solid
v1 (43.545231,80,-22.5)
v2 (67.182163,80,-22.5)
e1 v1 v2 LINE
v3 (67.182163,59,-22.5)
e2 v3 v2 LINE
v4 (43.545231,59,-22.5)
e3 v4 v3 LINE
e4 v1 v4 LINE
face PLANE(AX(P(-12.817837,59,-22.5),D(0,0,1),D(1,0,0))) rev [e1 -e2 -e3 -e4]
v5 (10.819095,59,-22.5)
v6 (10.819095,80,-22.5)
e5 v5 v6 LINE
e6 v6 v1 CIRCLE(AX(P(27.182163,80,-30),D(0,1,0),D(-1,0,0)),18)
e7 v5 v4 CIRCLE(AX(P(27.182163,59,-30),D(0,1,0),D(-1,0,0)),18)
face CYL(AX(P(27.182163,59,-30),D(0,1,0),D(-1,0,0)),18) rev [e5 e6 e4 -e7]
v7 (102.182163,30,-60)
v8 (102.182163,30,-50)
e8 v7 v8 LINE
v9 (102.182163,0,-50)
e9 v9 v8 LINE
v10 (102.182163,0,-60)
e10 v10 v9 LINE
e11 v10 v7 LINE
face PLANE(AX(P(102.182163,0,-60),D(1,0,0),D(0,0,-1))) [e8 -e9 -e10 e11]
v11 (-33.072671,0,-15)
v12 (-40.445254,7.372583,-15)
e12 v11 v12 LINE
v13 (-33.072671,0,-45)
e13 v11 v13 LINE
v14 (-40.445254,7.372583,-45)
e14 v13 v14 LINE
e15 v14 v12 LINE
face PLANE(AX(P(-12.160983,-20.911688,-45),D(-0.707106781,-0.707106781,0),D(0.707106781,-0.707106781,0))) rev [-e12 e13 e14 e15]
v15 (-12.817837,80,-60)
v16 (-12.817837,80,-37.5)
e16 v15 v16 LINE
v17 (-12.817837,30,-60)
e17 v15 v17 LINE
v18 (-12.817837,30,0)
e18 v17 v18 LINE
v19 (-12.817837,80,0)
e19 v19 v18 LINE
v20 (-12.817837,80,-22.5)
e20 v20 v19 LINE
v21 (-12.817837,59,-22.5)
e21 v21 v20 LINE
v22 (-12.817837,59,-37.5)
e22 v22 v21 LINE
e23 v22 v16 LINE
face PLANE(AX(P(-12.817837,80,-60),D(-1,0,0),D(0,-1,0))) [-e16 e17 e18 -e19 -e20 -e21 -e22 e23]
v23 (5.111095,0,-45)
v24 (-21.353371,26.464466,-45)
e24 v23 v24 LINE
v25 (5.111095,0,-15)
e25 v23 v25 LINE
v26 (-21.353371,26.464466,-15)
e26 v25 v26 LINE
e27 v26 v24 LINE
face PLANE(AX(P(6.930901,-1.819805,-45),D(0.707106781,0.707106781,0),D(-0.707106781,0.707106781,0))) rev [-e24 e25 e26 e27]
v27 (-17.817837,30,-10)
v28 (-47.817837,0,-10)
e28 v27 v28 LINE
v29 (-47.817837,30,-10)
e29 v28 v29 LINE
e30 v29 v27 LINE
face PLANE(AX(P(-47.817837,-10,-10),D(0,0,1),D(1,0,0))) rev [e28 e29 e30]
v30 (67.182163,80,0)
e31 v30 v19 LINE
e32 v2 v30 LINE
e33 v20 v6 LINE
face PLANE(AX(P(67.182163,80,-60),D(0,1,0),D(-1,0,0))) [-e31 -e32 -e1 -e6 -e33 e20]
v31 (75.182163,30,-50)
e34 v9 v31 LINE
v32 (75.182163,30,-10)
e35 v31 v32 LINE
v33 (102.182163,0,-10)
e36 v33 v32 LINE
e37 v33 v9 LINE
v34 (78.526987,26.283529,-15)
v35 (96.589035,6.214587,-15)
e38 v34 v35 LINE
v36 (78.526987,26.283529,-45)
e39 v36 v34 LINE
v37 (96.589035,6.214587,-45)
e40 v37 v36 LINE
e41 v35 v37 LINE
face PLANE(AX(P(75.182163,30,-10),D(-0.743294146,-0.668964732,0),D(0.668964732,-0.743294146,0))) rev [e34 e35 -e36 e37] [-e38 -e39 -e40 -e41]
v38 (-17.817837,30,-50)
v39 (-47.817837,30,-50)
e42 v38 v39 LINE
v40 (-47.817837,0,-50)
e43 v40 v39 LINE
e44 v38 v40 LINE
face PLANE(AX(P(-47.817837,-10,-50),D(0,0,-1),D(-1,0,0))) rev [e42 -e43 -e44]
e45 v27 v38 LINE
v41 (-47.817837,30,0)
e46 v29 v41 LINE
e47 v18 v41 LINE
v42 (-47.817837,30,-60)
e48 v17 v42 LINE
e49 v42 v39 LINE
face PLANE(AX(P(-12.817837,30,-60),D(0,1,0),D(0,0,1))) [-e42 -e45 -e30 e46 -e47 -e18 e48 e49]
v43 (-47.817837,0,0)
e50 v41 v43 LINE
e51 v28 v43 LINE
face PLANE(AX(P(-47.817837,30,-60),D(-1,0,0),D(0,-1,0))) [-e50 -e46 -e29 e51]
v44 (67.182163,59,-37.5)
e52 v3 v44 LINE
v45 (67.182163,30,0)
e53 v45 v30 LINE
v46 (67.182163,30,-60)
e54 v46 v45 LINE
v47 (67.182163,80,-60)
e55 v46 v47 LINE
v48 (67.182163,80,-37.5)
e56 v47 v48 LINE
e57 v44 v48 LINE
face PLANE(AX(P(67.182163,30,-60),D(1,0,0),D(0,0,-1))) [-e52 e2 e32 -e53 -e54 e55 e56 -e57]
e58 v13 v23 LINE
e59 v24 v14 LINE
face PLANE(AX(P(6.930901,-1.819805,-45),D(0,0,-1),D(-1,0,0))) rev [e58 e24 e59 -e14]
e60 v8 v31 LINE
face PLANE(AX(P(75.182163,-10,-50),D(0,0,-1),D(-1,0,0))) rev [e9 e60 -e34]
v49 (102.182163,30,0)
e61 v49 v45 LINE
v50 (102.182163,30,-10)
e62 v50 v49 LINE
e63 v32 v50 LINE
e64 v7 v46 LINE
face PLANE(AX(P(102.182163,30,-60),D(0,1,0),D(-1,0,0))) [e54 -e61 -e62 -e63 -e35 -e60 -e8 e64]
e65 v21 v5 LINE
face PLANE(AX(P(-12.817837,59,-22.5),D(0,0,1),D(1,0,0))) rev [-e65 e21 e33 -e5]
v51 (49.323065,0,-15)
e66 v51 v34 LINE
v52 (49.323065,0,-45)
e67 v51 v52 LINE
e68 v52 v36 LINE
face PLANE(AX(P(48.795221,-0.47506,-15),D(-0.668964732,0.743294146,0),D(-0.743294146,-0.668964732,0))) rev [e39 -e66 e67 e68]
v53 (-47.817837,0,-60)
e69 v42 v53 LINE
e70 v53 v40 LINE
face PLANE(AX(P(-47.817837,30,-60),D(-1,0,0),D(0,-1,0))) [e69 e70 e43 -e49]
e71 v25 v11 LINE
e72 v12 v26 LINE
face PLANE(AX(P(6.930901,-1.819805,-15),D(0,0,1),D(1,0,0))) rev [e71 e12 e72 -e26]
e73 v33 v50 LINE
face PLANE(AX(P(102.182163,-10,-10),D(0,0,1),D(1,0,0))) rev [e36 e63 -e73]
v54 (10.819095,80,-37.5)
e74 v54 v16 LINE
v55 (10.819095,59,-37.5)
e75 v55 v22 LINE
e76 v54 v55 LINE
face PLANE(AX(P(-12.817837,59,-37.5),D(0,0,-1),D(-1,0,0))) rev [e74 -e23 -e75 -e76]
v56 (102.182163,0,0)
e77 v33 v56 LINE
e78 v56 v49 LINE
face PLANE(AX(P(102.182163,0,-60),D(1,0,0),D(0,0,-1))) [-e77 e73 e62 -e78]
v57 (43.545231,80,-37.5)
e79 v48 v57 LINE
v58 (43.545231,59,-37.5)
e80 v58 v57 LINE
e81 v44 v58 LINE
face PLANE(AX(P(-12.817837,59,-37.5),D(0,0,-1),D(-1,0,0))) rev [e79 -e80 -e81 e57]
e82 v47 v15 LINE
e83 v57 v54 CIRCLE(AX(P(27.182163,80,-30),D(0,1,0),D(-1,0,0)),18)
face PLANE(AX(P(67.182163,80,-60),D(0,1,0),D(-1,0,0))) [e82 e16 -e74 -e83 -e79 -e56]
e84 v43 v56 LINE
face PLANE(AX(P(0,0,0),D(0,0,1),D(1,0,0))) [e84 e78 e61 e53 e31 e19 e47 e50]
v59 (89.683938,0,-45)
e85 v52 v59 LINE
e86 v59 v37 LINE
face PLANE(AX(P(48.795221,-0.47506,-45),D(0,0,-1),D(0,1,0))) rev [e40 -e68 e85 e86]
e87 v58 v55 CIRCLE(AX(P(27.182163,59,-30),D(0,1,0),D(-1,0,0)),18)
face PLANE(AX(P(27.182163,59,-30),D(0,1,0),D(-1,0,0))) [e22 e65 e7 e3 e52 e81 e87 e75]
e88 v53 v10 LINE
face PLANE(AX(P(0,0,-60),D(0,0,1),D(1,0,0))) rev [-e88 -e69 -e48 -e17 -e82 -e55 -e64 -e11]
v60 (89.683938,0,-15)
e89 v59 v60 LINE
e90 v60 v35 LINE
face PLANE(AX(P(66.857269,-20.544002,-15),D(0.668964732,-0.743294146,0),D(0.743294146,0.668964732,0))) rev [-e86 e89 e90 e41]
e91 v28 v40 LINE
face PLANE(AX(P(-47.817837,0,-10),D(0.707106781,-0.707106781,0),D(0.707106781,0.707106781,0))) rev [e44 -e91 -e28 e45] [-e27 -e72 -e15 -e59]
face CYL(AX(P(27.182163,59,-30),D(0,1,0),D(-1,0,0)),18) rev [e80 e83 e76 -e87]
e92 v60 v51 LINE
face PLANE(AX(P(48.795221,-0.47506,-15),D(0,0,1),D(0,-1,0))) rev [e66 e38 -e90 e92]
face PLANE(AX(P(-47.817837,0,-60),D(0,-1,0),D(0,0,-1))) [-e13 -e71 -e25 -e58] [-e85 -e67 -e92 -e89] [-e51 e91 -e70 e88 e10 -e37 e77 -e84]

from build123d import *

# Parameters (mm, degrees)
BASE_BLOCK_DEPTH           = 60
BORE_SKETCH_R              = 18
HALF_BORE_CUT_DEPTH        = 21
TOP_SLOT_SKETCH_W          = 80
TOP_SLOT_SKETCH_H          = 15
TOP_SLOT_CUT_DEPTH         = 21
SIDE_POCKET_A_SKETCH_W     = 27
SIDE_POCKET_A_SKETCH_H     = 40
SIDE_POCKET_A_DEPTH        = 40
FRAME_INFILL_A_DEPTH       = 40
TRIANGLE_WINDOW_A_SKETCH_W = 30
TRIANGLE_WINDOW_A_SKETCH_H = 27
TRIANGLE_WINDOW_A_DEPTH    = 40
SIDE_POCKET_B_SKETCH_W     = 30
SIDE_POCKET_B_SKETCH_H     = 40
SIDE_POCKET_B_DEPTH        = 40
FRAME_INFILL_B_DEPTH       = 40
TRIANGLE_WINDOW_B_SKETCH_W = 30
TRIANGLE_WINDOW_B_SKETCH_H = 27
TRIANGLE_WINDOW_B_DEPTH    = 40


with BuildPart() as part:
    # Base Profile Sketch → Base Block (new body)
    with BuildSketch(Plane.XY):
        Polygon((-47.817836812, 0), (102.182163188, 0), (102.182163188, 30), (67.182163188, 30), (67.182163188, 80), (-12.817836812, 80), (-12.817836812, 30), (-47.817836812, 30), align=None)
    extrude(amount=-BASE_BLOCK_DEPTH)

    # Bore Sketch → Half Bore Cut (cut)
    with BuildSketch(Plane(origin=(0, 80, 0), x_dir=(1, 0, 0), z_dir=(0, 1, 0))):
        with Locations(Location((27.182163188, 30, 0), (0, 0, 180))):
            Circle(BORE_SKETCH_R)
    extrude(amount=-HALF_BORE_CUT_DEPTH, mode=Mode.SUBTRACT)

    # Top Slot Sketch → Top Slot Cut (cut)
    with BuildSketch(Plane(origin=(0, 80, 0), x_dir=(1, 0, 0), z_dir=(0, 1, 0))):
        with Locations((27.182163188, 30)):
            Rectangle(TOP_SLOT_SKETCH_W, TOP_SLOT_SKETCH_H)
    extrude(amount=-TOP_SLOT_CUT_DEPTH, mode=Mode.SUBTRACT)

    # Side Pocket A Sketch → Side Pocket A (cut)
    with BuildSketch(Plane(origin=(0, 30, 0), x_dir=(1, 0, 0), z_dir=(0, 1, 0))):
        with Locations((88.682163188, 30)):
            Rectangle(SIDE_POCKET_A_SKETCH_W, SIDE_POCKET_A_SKETCH_H)
    extrude(amount=-SIDE_POCKET_A_DEPTH, mode=Mode.SUBTRACT)

    # Frame Infill A Sketch → Frame Infill A (add)
    with BuildSketch(Plane.XY.offset(-50)):
        Polygon((75.182163188, 30), (102.182163188, 0), (75.182163188, 0), align=None)
    extrude(amount=FRAME_INFILL_A_DEPTH)

    # Triangle Window A Sketch → Triangle Window A (cut)
    with BuildSketch(Plane(origin=(56.454233805, 50.808810425, 0), x_dir=(0, 0, -1), z_dir=(0.7432941462471663, 0.6689647316224498, 0))):
        with Locations((30, -46.495391232)):
            Rectangle(TRIANGLE_WINDOW_A_SKETCH_W, TRIANGLE_WINDOW_A_SKETCH_H)
    extrude(amount=-TRIANGLE_WINDOW_A_DEPTH, mode=Mode.SUBTRACT)

    # Side Pocket B Sketch → Side Pocket B (cut)
    with BuildSketch(Plane(origin=(0, 30, 0), x_dir=(1, 0, 0), z_dir=(0, 1, 0))):
        with Locations((-32.817836812, 30)):
            Rectangle(SIDE_POCKET_B_SKETCH_W, SIDE_POCKET_B_SKETCH_H)
    extrude(amount=-SIDE_POCKET_B_DEPTH, mode=Mode.SUBTRACT)

    # Frame Infill B Sketch → Frame Infill B (add)
    with BuildSketch(Plane.XY.offset(-50)):
        Polygon((-47.817836812, 0), (-17.817836812, 30), (-17.817836812, 0), align=None)
    extrude(amount=FRAME_INFILL_B_DEPTH)

    # Triangle Window B Sketch → Triangle Window B (cut)
    with BuildSketch(Plane(origin=(-23.908918406, 23.908918406, 0), x_dir=(0, 0, 1), z_dir=(-0.7071067811865476, 0.7071067811865476, 0))):
        with Locations((-30, -9.8859098)):
            Rectangle(TRIANGLE_WINDOW_B_SKETCH_W, TRIANGLE_WINDOW_B_SKETCH_H)
    extrude(amount=-TRIANGLE_WINDOW_B_DEPTH, mode=Mode.SUBTRACT)


solid = part.part
